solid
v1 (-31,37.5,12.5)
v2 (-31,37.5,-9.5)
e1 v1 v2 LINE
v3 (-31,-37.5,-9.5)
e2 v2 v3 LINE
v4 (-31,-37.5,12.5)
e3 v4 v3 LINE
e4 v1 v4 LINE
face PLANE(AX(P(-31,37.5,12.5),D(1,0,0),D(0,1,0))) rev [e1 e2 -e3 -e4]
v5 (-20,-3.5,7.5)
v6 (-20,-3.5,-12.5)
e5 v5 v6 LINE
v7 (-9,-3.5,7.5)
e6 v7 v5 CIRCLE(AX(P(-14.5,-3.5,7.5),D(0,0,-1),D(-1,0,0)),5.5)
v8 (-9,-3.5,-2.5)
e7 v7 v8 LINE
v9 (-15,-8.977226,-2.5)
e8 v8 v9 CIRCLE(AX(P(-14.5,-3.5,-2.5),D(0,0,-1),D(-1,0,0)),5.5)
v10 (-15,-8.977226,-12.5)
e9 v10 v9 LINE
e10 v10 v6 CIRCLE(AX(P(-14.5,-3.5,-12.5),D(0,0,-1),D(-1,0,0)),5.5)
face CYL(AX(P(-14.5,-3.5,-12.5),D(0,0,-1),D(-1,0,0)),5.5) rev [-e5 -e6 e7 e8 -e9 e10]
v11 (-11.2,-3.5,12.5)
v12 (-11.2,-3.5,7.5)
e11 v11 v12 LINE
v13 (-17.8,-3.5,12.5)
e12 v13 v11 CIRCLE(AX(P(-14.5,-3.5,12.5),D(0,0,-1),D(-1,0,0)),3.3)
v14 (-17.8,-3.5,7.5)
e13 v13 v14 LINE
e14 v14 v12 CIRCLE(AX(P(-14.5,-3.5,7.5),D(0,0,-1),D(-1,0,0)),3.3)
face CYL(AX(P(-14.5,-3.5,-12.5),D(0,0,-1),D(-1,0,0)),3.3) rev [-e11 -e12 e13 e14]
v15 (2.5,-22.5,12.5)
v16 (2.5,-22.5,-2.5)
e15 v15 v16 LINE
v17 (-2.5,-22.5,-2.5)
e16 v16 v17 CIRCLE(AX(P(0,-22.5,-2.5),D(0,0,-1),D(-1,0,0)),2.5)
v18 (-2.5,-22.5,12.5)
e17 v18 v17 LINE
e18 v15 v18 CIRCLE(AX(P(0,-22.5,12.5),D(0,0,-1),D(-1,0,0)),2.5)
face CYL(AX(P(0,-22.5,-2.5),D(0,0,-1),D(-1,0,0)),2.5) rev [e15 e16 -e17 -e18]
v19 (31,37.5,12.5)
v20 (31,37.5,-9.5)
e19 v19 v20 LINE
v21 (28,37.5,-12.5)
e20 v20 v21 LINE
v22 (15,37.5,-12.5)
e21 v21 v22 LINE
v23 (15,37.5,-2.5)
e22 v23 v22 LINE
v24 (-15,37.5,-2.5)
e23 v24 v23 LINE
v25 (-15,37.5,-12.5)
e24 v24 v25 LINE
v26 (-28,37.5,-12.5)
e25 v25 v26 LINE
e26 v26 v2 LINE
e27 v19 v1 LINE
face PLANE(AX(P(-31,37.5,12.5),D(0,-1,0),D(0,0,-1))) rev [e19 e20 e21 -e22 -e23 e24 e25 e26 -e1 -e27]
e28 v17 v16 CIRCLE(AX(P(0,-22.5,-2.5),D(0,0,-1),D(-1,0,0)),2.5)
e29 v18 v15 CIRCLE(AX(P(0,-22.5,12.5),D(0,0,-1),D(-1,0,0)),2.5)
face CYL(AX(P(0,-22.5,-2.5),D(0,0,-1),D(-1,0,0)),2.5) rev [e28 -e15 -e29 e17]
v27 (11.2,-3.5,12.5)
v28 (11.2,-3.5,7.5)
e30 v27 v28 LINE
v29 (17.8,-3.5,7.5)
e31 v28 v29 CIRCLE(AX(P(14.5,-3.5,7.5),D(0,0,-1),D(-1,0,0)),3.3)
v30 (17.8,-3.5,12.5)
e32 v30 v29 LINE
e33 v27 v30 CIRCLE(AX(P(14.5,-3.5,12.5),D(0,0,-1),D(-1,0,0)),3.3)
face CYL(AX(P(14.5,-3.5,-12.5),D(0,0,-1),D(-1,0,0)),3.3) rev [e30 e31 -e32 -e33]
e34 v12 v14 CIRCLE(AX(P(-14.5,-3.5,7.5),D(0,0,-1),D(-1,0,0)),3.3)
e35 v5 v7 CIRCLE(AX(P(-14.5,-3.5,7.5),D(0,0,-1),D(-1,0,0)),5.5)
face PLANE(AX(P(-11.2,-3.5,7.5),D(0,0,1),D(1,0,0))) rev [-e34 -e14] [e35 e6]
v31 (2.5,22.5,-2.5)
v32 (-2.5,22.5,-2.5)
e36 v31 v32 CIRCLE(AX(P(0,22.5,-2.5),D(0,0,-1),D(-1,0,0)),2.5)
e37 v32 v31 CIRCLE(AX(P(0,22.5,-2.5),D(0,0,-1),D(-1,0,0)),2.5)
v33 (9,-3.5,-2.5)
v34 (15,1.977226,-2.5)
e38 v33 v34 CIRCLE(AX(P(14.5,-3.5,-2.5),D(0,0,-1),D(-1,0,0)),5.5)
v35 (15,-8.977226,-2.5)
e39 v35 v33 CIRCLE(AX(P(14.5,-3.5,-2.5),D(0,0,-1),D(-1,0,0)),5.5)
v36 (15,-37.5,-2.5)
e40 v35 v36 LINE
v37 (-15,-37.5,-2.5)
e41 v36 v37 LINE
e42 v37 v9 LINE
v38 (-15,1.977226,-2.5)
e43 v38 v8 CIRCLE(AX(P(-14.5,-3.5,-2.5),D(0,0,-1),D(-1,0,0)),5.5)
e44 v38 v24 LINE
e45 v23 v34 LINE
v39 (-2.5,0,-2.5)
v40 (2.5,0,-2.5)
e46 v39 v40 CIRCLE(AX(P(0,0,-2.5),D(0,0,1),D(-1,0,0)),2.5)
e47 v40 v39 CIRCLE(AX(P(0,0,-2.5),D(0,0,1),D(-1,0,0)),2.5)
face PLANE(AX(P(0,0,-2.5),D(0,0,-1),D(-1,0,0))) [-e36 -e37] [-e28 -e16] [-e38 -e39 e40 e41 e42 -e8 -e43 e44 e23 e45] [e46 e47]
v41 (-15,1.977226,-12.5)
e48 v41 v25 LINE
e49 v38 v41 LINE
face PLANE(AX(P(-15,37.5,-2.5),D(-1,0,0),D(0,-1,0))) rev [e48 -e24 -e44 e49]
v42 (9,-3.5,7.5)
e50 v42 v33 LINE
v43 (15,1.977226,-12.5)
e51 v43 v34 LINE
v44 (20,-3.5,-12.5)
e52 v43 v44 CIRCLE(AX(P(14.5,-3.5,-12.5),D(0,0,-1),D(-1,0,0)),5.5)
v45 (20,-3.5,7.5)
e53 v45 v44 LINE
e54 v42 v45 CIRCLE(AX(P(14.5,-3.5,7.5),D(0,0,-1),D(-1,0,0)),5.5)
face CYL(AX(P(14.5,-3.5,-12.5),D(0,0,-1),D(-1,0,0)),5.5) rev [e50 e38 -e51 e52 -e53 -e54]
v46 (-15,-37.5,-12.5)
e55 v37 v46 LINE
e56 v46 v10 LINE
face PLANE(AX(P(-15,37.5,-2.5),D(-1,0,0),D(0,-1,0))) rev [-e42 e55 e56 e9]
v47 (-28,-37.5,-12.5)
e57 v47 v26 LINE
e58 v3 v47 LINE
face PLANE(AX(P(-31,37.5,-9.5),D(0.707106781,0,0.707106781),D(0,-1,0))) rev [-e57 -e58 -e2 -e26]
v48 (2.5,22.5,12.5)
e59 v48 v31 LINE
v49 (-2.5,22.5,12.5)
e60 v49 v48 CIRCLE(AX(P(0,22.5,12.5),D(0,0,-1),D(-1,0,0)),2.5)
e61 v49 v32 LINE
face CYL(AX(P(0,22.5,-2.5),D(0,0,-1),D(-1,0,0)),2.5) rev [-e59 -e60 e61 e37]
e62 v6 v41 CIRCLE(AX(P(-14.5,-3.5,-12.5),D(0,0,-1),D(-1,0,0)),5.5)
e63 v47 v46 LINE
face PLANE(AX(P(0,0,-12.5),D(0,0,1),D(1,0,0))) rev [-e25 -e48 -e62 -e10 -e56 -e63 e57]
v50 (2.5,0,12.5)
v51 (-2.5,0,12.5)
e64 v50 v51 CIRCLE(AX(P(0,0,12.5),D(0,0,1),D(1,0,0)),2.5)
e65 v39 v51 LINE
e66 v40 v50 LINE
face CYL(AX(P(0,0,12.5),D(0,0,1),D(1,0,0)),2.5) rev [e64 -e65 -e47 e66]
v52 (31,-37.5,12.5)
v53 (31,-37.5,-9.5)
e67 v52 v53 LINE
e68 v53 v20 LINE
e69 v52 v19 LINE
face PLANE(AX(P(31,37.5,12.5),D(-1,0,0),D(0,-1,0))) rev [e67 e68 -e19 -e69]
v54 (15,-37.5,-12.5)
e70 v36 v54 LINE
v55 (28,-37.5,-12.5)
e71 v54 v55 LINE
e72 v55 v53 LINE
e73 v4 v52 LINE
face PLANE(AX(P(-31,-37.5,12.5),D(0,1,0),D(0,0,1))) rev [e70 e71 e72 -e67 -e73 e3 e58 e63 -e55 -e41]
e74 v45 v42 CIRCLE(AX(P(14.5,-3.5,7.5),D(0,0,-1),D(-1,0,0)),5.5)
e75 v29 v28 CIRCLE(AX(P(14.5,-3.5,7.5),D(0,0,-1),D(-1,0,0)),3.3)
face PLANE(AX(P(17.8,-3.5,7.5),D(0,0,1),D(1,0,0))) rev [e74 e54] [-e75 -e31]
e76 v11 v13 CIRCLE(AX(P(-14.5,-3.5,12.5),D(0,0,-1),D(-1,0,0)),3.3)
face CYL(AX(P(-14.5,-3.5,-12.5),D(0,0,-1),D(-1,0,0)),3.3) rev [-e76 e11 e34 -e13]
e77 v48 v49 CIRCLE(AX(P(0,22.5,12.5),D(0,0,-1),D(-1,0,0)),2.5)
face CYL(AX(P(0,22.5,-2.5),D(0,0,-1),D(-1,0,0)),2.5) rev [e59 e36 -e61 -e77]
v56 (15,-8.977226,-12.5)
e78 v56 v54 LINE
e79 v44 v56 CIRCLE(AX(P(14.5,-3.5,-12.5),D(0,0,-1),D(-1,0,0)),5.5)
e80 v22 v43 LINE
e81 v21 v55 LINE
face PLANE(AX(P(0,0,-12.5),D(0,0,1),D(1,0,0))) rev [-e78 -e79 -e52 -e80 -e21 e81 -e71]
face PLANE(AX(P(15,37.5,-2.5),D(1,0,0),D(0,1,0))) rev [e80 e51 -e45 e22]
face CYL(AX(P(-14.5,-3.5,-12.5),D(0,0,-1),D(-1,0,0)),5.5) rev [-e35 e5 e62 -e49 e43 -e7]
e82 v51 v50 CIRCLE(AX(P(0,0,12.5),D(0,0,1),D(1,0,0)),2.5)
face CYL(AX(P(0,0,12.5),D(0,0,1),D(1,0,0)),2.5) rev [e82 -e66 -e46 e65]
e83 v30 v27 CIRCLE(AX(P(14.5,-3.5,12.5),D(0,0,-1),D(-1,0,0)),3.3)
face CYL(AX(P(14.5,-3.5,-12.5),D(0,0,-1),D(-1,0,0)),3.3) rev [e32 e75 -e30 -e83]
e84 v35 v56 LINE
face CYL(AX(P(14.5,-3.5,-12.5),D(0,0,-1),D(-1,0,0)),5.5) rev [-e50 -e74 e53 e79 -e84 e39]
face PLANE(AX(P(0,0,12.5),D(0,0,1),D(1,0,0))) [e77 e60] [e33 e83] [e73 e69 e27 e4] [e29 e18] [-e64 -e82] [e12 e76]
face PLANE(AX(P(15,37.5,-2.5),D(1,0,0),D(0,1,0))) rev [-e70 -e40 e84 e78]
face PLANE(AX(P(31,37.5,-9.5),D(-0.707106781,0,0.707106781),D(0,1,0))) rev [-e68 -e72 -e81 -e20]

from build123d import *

# Parameters (mm, degrees)
SKETCH_1_W                     = 62
SKETCH_1_H                     = 75
EXTRUDE_1_DEPTH                = 12.5
HOLE_WIZARD_M6_1_D             = 5
CHAMFER_1_SIZE                 = 3
SKETCH_8_W                     = 30
SKETCH_8_H                     = 75
CUT_EXTRUDE_1_DEPTH            = 10
HOLE_WIZARD_M6_2_D             = 5
HOLE_WIZARD_M6_1_2_D           = 6.6
HOLE_WIZARD_M6_1_2_CBORE_D     = 11
HOLE_WIZARD_M6_1_2_CBORE_DEPTH = 20


with BuildPart() as part:
    # 草图1 → 凸台-拉伸1 (new, symmetric)
    with BuildSketch(Plane.XY):
        Rectangle(SKETCH_1_W, SKETCH_1_H)
    extrude(amount=EXTRUDE_1_DEPTH, both=True)

    # Hole Wizard M6 _1 (through all)
    with Locations(Plane.XY.offset(12.5)):
        with Locations((0, 0)):
            Hole(HOLE_WIZARD_M6_1_D / 2)

    # 倒角1
    chamfer_1_edges = [part.edges().sort_by_distance(p)[0] for p in [
        (-31, 0, -12.5),
        (31, 0, -12.5),
    ]]
    chamfer(chamfer_1_edges, length=CHAMFER_1_SIZE)

    # 草图8 → 切除-拉伸1 (cut)
    with BuildSketch(Plane(origin=(0, 0, -12.5), x_dir=(-1, 0, 0), z_dir=(0, 0, -1))):
        Rectangle(SKETCH_8_W, SKETCH_8_H)
    extrude(amount=-CUT_EXTRUDE_1_DEPTH, mode=Mode.SUBTRACT)

    # M6 螺纹孔2 (through all)
    with Locations(Plane(origin=(0, 0, -2.5), x_dir=(-1, 0, 0), z_dir=(0, 0, -1))):
        with Locations((0, 22.5), (0, -22.5)):
            Hole(HOLE_WIZARD_M6_2_D / 2)

    # Hole Wizard M6 _1 2 (through all)
    with Locations(Plane(origin=(0, 0, -12.5), x_dir=(-1, 0, 0), z_dir=(0, 0, -1))):
        with Locations((-14.5, -3.5), (14.5, -3.5)):
            CounterBoreHole(HOLE_WIZARD_M6_1_2_D / 2, HOLE_WIZARD_M6_1_2_CBORE_D / 2, HOLE_WIZARD_M6_1_2_CBORE_DEPTH)


solid = part.part
